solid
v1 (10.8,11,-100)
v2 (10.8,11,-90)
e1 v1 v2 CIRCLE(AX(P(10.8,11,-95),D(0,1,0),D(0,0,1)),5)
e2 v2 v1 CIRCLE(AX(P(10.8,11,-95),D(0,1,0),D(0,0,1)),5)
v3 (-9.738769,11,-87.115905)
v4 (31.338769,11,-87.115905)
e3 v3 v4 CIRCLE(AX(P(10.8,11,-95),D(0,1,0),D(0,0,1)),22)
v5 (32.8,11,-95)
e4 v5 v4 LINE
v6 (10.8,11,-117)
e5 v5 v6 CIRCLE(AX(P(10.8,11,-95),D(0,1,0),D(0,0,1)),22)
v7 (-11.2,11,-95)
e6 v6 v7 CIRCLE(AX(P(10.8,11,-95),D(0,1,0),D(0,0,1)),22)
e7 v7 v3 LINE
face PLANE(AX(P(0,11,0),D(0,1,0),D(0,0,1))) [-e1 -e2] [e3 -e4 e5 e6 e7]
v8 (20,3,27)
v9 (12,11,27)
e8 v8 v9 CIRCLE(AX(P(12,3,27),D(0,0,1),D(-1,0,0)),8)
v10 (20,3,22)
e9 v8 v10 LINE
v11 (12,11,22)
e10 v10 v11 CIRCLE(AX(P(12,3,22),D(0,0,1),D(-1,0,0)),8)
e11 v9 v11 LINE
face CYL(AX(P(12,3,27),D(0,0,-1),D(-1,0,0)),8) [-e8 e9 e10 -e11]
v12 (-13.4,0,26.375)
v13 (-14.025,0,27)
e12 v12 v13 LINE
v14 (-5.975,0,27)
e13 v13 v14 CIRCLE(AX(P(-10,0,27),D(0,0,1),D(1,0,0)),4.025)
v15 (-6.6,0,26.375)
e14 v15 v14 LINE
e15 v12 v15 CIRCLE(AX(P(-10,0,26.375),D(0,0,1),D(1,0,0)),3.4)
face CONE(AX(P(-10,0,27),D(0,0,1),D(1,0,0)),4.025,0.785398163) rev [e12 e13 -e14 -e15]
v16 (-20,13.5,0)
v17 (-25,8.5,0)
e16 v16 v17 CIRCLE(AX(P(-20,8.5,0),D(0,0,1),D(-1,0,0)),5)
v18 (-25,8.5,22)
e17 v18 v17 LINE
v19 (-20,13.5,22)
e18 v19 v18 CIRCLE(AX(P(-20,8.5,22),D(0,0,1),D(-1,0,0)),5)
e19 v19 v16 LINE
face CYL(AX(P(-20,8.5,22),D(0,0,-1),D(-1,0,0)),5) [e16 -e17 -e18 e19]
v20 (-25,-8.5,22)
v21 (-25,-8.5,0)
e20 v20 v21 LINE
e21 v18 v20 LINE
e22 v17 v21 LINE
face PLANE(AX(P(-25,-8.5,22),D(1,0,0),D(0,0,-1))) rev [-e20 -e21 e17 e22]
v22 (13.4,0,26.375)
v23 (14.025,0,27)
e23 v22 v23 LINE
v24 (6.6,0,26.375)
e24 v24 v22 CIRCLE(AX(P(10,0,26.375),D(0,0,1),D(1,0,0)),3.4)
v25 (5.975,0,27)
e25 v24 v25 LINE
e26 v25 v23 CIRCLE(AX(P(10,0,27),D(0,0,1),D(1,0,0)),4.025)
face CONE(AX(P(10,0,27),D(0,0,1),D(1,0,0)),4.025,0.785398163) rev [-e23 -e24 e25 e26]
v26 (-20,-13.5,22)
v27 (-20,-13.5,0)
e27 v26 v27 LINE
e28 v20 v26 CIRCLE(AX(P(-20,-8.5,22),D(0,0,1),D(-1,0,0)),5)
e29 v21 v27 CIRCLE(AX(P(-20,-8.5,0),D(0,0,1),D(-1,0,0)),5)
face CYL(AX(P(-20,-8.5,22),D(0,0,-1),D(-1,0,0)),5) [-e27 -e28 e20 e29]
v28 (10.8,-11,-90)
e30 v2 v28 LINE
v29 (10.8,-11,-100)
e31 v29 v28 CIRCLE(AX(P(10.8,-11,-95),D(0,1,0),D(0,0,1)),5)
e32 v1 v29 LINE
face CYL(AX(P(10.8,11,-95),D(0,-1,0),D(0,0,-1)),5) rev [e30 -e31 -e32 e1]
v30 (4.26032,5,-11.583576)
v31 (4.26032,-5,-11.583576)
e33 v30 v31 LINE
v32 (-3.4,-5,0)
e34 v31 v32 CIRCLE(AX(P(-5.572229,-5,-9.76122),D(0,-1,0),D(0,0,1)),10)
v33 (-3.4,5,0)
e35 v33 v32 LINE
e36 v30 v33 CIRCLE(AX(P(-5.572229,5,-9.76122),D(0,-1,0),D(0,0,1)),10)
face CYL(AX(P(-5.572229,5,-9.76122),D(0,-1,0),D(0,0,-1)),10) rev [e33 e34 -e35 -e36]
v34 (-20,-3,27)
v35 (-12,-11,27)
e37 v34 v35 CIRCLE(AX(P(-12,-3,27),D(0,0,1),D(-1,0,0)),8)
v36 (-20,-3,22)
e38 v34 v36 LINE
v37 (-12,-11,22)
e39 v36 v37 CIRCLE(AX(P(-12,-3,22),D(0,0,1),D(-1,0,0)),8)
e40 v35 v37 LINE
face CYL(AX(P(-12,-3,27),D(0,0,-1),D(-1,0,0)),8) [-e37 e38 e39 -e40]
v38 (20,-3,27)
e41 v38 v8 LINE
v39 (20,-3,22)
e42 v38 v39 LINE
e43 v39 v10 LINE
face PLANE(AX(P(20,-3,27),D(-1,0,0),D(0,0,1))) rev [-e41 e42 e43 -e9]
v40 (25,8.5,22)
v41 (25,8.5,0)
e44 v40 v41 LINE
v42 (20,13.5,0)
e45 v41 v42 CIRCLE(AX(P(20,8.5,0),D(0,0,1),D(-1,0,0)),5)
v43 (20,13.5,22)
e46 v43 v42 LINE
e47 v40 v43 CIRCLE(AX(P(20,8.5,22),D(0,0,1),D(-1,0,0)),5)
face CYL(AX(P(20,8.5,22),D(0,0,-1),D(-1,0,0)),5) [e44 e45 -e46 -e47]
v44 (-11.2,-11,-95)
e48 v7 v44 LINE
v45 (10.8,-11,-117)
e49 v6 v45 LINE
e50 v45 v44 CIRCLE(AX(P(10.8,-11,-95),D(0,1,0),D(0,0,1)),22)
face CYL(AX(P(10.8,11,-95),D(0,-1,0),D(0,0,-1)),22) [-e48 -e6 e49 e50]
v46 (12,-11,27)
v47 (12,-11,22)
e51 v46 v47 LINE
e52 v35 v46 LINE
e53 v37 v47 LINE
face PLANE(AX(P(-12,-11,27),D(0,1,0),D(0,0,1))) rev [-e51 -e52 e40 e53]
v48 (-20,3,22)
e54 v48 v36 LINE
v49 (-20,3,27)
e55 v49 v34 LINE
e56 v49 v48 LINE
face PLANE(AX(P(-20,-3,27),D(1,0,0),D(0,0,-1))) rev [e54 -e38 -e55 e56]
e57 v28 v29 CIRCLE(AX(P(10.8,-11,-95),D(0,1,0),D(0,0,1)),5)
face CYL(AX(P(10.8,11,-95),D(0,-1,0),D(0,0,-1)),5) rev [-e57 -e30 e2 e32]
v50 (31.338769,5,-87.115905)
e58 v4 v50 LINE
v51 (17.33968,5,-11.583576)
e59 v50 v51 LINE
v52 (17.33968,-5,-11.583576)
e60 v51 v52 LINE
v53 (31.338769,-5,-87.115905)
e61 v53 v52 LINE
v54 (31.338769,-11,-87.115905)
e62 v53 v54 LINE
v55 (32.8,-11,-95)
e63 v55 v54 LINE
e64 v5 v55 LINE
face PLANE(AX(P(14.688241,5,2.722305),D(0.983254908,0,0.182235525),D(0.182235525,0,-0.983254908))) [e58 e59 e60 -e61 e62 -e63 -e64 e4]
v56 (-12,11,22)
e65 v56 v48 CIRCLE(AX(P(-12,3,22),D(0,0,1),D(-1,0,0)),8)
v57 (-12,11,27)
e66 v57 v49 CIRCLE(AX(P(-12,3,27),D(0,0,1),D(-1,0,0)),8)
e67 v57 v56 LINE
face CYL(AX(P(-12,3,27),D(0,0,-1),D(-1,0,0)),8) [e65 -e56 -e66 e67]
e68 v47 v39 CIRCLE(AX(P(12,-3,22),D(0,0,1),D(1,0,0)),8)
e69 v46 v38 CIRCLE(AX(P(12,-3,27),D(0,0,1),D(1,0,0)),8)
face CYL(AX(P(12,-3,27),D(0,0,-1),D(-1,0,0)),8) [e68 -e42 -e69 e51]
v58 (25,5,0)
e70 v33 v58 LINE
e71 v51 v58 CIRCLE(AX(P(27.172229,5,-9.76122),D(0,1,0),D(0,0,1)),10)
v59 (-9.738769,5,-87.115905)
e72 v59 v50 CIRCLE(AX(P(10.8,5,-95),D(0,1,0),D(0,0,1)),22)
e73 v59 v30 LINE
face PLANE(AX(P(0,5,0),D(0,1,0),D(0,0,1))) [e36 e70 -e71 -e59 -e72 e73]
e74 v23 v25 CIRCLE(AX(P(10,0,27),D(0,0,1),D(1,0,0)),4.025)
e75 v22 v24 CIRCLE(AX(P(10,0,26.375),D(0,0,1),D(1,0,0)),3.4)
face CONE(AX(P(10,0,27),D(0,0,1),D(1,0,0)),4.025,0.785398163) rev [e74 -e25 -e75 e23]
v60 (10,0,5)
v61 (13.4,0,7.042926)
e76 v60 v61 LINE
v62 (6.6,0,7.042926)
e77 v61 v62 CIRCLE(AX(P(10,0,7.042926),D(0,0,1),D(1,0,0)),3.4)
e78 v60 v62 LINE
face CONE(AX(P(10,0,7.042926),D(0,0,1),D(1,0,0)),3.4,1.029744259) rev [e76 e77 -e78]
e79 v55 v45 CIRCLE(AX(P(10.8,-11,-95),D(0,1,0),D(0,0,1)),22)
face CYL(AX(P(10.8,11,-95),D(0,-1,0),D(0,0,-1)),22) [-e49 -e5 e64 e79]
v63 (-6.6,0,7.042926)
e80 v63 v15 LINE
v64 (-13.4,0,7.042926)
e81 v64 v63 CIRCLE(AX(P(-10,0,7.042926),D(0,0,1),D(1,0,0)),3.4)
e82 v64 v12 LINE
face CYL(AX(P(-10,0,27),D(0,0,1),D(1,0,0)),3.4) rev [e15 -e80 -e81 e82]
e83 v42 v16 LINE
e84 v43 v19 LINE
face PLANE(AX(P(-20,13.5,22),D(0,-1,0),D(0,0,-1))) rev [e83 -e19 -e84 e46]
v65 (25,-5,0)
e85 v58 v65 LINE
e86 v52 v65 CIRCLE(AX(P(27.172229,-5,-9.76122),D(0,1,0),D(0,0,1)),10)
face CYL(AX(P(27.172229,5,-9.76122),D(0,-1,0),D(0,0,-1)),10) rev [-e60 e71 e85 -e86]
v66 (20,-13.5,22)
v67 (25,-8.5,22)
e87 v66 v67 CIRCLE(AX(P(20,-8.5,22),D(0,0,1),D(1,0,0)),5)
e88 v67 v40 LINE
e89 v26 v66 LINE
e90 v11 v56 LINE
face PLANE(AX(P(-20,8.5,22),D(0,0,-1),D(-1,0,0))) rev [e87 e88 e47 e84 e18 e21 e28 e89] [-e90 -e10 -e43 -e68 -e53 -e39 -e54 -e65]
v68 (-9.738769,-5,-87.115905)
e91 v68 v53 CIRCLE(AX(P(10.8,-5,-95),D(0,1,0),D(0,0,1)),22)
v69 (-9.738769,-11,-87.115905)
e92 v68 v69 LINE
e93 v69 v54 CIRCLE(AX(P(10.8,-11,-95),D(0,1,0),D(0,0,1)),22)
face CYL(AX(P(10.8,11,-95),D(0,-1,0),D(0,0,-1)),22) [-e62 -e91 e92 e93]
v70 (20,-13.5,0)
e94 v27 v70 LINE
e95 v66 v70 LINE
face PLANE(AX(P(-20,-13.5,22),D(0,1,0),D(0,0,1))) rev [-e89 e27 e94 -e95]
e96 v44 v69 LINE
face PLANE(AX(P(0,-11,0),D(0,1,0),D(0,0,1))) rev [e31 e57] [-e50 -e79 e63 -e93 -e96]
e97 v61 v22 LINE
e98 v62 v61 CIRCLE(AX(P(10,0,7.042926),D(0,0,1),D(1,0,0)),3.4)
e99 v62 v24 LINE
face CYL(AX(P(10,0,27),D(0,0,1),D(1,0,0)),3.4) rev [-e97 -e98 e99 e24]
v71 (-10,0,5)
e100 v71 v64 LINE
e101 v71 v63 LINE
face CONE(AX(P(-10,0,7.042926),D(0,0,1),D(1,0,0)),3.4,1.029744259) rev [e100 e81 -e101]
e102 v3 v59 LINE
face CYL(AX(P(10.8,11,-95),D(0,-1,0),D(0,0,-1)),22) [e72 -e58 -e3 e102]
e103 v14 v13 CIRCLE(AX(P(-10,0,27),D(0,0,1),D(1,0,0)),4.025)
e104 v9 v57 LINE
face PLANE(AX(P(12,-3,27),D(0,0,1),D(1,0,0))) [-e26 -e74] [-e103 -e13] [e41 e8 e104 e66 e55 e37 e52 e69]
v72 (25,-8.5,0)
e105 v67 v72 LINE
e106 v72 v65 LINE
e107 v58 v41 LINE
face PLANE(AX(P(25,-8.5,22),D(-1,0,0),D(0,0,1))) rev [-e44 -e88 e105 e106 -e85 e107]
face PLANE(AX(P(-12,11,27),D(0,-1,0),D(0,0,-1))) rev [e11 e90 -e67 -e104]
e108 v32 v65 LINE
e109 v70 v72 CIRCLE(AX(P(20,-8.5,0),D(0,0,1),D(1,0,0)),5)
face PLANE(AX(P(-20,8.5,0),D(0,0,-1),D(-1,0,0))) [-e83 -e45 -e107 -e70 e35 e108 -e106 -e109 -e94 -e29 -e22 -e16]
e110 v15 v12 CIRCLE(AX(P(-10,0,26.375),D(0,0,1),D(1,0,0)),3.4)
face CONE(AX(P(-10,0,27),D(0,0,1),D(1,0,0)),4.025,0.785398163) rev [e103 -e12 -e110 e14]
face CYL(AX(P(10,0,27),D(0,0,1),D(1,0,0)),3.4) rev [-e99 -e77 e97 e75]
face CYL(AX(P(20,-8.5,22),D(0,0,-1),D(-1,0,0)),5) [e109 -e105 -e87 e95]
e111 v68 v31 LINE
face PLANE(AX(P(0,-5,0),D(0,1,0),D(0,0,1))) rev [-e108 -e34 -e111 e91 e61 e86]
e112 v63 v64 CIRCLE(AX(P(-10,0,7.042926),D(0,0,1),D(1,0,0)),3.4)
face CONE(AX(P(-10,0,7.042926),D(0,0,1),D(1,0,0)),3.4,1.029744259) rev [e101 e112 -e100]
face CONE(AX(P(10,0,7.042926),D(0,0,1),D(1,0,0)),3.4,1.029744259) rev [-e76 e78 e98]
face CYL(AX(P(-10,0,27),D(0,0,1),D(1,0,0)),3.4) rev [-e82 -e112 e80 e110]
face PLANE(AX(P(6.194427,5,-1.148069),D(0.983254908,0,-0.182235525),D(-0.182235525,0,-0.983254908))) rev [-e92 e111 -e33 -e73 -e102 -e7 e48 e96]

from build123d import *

# Parameters (mm, degrees)
BOSS_EXTRUDE1_DEPTH         = 22
BOSS_EXTRUDE2_DEPTH         = 5
BOSS_EXTRUDE3_DEPTH         = 5
SKETCH_4_3_2_R              = 5
BOSS_EXTRUDE4_DEPTH         = 11
M8_TAPPED_HOLE1_D           = 6.8
M8_TAPPED_HOLE1_DEPTH       = 19.957073895
M8_TAPPED_HOLE1_CSINK_D     = 8.05
M8_TAPPED_HOLE1_CSINK_ANGLE = 90
M8_TAPPED_HOLE1_TIP         = 2.042926105


with BuildPart() as part:
    # Sketch1 → Boss-Extrude1 (new body)
    with BuildSketch(Plane.XY):
        with BuildLine():
            Line((-20, -13.5), (20, -13.5))
            ThreePointArc((20, -13.5), (23.535533906, -12.035533906), (25, -8.5))
            Line((25, -8.5), (25, 8.5))
            ThreePointArc((25, 8.5), (23.535533906, 12.035533906), (20, 13.5))
            Line((20, 13.5), (-20, 13.5))
            ThreePointArc((-20, 13.5), (-23.535533906, 12.035533906), (-25, 8.5))
            Line((-25, 8.5), (-25, -8.5))
            ThreePointArc((-25, -8.5), (-23.535533906, -12.035533906), (-20, -13.5))
        make_face()
    extrude(amount=BOSS_EXTRUDE1_DEPTH)

    # Sketch2 → Boss-Extrude2 (add)
    with BuildSketch(Plane.XY.offset(22)):
        with BuildLine():
            Line((-12, -11), (12, -11))
            ThreePointArc((12, -11), (17.656854249, -8.656854249), (20, -3))
            Line((20, -3), (20, 3))
            ThreePointArc((20, 3), (17.656854249, 8.656854249), (12, 11))
            Line((12, 11), (-12, 11))
            ThreePointArc((-12, 11), (-17.656854249, 8.656854249), (-20, 3))
            Line((-20, 3), (-20, -3))
            ThreePointArc((-20, -3), (-17.656854249, -8.656854249), (-12, -11))
        make_face()
    extrude(amount=BOSS_EXTRUDE2_DEPTH)

    # Sketch 4_3 → Boss-Extrude3 (add, symmetric)
    with BuildSketch(Plane(origin=(0, 0, 0), x_dir=(1, 0, 0), z_dir=(0, 1, 0))):
        with BuildLine():
            ThreePointArc((31.338769383, 87.11590511), (23.260937212, 76.86922385), (10.8, 73))
            Line((10.8, 73), (10.8, 0))
            Line((10.8, 0), (25, 0))
            ThreePointArc((25, 0), (18.831156894, 4.245196236), (17.339679571, 11.583575604))
            Line((17.339679571, 11.583575604), (31.338769383, 87.11590511))
        make_face()
        with BuildLine():
            ThreePointArc((10.8, 73), (-1.660937212, 76.86922385), (-9.738769383, 87.11590511))
            Line((-9.738769383, 87.11590511), (4.260320429, 11.583575604))
            ThreePointArc((4.260320429, 11.583575604), (2.768843106, 4.245196236), (-3.4, 0))
            Line((-3.4, 0), (10.8, 0))
            Line((10.8, 0), (10.8, 73))
        make_face()
    extrude(amount=BOSS_EXTRUDE3_DEPTH, both=True)

    # Sketch 4_3 2 → Boss-Extrude4 (add, symmetric)
    with BuildSketch(Plane(origin=(0, 0, 0), x_dir=(1, 0, 0), z_dir=(0, 1, 0))):
        with BuildLine():
            ThreePointArc((32.8, 95), (10.8, 117), (-11.2, 95))
            Line((-11.2, 95), (-9.738769383, 87.11590511))
            ThreePointArc((-9.738769383, 87.11590511), (10.8, 73), (31.338769383, 87.11590511))
            Line((31.338769383, 87.11590511), (32.8, 95))
        make_face()
        with Locations(Location((10.8, 95, 0), (0, 0, 270))):
            Circle(SKETCH_4_3_2_R, mode=Mode.SUBTRACT)
    extrude(amount=BOSS_EXTRUDE4_DEPTH, both=True)

    # M8 Tapped Hole1
    with Locations(Plane(origin=(-10, 0, 27), x_dir=(1, 0, 0), z_dir=(0, 0, 1))):
        with Locations((0, 0), (20, 0)):
            CounterSinkHole(M8_TAPPED_HOLE1_D / 2, M8_TAPPED_HOLE1_CSINK_D / 2, depth=M8_TAPPED_HOLE1_DEPTH, counter_sink_angle=M8_TAPPED_HOLE1_CSINK_ANGLE)
            with Locations((0, 0, -(M8_TAPPED_HOLE1_DEPTH + M8_TAPPED_HOLE1_TIP / 2))):  # 118° drill point
                Cone(0, M8_TAPPED_HOLE1_D / 2, M8_TAPPED_HOLE1_TIP, mode=Mode.SUBTRACT)


solid = part.part
